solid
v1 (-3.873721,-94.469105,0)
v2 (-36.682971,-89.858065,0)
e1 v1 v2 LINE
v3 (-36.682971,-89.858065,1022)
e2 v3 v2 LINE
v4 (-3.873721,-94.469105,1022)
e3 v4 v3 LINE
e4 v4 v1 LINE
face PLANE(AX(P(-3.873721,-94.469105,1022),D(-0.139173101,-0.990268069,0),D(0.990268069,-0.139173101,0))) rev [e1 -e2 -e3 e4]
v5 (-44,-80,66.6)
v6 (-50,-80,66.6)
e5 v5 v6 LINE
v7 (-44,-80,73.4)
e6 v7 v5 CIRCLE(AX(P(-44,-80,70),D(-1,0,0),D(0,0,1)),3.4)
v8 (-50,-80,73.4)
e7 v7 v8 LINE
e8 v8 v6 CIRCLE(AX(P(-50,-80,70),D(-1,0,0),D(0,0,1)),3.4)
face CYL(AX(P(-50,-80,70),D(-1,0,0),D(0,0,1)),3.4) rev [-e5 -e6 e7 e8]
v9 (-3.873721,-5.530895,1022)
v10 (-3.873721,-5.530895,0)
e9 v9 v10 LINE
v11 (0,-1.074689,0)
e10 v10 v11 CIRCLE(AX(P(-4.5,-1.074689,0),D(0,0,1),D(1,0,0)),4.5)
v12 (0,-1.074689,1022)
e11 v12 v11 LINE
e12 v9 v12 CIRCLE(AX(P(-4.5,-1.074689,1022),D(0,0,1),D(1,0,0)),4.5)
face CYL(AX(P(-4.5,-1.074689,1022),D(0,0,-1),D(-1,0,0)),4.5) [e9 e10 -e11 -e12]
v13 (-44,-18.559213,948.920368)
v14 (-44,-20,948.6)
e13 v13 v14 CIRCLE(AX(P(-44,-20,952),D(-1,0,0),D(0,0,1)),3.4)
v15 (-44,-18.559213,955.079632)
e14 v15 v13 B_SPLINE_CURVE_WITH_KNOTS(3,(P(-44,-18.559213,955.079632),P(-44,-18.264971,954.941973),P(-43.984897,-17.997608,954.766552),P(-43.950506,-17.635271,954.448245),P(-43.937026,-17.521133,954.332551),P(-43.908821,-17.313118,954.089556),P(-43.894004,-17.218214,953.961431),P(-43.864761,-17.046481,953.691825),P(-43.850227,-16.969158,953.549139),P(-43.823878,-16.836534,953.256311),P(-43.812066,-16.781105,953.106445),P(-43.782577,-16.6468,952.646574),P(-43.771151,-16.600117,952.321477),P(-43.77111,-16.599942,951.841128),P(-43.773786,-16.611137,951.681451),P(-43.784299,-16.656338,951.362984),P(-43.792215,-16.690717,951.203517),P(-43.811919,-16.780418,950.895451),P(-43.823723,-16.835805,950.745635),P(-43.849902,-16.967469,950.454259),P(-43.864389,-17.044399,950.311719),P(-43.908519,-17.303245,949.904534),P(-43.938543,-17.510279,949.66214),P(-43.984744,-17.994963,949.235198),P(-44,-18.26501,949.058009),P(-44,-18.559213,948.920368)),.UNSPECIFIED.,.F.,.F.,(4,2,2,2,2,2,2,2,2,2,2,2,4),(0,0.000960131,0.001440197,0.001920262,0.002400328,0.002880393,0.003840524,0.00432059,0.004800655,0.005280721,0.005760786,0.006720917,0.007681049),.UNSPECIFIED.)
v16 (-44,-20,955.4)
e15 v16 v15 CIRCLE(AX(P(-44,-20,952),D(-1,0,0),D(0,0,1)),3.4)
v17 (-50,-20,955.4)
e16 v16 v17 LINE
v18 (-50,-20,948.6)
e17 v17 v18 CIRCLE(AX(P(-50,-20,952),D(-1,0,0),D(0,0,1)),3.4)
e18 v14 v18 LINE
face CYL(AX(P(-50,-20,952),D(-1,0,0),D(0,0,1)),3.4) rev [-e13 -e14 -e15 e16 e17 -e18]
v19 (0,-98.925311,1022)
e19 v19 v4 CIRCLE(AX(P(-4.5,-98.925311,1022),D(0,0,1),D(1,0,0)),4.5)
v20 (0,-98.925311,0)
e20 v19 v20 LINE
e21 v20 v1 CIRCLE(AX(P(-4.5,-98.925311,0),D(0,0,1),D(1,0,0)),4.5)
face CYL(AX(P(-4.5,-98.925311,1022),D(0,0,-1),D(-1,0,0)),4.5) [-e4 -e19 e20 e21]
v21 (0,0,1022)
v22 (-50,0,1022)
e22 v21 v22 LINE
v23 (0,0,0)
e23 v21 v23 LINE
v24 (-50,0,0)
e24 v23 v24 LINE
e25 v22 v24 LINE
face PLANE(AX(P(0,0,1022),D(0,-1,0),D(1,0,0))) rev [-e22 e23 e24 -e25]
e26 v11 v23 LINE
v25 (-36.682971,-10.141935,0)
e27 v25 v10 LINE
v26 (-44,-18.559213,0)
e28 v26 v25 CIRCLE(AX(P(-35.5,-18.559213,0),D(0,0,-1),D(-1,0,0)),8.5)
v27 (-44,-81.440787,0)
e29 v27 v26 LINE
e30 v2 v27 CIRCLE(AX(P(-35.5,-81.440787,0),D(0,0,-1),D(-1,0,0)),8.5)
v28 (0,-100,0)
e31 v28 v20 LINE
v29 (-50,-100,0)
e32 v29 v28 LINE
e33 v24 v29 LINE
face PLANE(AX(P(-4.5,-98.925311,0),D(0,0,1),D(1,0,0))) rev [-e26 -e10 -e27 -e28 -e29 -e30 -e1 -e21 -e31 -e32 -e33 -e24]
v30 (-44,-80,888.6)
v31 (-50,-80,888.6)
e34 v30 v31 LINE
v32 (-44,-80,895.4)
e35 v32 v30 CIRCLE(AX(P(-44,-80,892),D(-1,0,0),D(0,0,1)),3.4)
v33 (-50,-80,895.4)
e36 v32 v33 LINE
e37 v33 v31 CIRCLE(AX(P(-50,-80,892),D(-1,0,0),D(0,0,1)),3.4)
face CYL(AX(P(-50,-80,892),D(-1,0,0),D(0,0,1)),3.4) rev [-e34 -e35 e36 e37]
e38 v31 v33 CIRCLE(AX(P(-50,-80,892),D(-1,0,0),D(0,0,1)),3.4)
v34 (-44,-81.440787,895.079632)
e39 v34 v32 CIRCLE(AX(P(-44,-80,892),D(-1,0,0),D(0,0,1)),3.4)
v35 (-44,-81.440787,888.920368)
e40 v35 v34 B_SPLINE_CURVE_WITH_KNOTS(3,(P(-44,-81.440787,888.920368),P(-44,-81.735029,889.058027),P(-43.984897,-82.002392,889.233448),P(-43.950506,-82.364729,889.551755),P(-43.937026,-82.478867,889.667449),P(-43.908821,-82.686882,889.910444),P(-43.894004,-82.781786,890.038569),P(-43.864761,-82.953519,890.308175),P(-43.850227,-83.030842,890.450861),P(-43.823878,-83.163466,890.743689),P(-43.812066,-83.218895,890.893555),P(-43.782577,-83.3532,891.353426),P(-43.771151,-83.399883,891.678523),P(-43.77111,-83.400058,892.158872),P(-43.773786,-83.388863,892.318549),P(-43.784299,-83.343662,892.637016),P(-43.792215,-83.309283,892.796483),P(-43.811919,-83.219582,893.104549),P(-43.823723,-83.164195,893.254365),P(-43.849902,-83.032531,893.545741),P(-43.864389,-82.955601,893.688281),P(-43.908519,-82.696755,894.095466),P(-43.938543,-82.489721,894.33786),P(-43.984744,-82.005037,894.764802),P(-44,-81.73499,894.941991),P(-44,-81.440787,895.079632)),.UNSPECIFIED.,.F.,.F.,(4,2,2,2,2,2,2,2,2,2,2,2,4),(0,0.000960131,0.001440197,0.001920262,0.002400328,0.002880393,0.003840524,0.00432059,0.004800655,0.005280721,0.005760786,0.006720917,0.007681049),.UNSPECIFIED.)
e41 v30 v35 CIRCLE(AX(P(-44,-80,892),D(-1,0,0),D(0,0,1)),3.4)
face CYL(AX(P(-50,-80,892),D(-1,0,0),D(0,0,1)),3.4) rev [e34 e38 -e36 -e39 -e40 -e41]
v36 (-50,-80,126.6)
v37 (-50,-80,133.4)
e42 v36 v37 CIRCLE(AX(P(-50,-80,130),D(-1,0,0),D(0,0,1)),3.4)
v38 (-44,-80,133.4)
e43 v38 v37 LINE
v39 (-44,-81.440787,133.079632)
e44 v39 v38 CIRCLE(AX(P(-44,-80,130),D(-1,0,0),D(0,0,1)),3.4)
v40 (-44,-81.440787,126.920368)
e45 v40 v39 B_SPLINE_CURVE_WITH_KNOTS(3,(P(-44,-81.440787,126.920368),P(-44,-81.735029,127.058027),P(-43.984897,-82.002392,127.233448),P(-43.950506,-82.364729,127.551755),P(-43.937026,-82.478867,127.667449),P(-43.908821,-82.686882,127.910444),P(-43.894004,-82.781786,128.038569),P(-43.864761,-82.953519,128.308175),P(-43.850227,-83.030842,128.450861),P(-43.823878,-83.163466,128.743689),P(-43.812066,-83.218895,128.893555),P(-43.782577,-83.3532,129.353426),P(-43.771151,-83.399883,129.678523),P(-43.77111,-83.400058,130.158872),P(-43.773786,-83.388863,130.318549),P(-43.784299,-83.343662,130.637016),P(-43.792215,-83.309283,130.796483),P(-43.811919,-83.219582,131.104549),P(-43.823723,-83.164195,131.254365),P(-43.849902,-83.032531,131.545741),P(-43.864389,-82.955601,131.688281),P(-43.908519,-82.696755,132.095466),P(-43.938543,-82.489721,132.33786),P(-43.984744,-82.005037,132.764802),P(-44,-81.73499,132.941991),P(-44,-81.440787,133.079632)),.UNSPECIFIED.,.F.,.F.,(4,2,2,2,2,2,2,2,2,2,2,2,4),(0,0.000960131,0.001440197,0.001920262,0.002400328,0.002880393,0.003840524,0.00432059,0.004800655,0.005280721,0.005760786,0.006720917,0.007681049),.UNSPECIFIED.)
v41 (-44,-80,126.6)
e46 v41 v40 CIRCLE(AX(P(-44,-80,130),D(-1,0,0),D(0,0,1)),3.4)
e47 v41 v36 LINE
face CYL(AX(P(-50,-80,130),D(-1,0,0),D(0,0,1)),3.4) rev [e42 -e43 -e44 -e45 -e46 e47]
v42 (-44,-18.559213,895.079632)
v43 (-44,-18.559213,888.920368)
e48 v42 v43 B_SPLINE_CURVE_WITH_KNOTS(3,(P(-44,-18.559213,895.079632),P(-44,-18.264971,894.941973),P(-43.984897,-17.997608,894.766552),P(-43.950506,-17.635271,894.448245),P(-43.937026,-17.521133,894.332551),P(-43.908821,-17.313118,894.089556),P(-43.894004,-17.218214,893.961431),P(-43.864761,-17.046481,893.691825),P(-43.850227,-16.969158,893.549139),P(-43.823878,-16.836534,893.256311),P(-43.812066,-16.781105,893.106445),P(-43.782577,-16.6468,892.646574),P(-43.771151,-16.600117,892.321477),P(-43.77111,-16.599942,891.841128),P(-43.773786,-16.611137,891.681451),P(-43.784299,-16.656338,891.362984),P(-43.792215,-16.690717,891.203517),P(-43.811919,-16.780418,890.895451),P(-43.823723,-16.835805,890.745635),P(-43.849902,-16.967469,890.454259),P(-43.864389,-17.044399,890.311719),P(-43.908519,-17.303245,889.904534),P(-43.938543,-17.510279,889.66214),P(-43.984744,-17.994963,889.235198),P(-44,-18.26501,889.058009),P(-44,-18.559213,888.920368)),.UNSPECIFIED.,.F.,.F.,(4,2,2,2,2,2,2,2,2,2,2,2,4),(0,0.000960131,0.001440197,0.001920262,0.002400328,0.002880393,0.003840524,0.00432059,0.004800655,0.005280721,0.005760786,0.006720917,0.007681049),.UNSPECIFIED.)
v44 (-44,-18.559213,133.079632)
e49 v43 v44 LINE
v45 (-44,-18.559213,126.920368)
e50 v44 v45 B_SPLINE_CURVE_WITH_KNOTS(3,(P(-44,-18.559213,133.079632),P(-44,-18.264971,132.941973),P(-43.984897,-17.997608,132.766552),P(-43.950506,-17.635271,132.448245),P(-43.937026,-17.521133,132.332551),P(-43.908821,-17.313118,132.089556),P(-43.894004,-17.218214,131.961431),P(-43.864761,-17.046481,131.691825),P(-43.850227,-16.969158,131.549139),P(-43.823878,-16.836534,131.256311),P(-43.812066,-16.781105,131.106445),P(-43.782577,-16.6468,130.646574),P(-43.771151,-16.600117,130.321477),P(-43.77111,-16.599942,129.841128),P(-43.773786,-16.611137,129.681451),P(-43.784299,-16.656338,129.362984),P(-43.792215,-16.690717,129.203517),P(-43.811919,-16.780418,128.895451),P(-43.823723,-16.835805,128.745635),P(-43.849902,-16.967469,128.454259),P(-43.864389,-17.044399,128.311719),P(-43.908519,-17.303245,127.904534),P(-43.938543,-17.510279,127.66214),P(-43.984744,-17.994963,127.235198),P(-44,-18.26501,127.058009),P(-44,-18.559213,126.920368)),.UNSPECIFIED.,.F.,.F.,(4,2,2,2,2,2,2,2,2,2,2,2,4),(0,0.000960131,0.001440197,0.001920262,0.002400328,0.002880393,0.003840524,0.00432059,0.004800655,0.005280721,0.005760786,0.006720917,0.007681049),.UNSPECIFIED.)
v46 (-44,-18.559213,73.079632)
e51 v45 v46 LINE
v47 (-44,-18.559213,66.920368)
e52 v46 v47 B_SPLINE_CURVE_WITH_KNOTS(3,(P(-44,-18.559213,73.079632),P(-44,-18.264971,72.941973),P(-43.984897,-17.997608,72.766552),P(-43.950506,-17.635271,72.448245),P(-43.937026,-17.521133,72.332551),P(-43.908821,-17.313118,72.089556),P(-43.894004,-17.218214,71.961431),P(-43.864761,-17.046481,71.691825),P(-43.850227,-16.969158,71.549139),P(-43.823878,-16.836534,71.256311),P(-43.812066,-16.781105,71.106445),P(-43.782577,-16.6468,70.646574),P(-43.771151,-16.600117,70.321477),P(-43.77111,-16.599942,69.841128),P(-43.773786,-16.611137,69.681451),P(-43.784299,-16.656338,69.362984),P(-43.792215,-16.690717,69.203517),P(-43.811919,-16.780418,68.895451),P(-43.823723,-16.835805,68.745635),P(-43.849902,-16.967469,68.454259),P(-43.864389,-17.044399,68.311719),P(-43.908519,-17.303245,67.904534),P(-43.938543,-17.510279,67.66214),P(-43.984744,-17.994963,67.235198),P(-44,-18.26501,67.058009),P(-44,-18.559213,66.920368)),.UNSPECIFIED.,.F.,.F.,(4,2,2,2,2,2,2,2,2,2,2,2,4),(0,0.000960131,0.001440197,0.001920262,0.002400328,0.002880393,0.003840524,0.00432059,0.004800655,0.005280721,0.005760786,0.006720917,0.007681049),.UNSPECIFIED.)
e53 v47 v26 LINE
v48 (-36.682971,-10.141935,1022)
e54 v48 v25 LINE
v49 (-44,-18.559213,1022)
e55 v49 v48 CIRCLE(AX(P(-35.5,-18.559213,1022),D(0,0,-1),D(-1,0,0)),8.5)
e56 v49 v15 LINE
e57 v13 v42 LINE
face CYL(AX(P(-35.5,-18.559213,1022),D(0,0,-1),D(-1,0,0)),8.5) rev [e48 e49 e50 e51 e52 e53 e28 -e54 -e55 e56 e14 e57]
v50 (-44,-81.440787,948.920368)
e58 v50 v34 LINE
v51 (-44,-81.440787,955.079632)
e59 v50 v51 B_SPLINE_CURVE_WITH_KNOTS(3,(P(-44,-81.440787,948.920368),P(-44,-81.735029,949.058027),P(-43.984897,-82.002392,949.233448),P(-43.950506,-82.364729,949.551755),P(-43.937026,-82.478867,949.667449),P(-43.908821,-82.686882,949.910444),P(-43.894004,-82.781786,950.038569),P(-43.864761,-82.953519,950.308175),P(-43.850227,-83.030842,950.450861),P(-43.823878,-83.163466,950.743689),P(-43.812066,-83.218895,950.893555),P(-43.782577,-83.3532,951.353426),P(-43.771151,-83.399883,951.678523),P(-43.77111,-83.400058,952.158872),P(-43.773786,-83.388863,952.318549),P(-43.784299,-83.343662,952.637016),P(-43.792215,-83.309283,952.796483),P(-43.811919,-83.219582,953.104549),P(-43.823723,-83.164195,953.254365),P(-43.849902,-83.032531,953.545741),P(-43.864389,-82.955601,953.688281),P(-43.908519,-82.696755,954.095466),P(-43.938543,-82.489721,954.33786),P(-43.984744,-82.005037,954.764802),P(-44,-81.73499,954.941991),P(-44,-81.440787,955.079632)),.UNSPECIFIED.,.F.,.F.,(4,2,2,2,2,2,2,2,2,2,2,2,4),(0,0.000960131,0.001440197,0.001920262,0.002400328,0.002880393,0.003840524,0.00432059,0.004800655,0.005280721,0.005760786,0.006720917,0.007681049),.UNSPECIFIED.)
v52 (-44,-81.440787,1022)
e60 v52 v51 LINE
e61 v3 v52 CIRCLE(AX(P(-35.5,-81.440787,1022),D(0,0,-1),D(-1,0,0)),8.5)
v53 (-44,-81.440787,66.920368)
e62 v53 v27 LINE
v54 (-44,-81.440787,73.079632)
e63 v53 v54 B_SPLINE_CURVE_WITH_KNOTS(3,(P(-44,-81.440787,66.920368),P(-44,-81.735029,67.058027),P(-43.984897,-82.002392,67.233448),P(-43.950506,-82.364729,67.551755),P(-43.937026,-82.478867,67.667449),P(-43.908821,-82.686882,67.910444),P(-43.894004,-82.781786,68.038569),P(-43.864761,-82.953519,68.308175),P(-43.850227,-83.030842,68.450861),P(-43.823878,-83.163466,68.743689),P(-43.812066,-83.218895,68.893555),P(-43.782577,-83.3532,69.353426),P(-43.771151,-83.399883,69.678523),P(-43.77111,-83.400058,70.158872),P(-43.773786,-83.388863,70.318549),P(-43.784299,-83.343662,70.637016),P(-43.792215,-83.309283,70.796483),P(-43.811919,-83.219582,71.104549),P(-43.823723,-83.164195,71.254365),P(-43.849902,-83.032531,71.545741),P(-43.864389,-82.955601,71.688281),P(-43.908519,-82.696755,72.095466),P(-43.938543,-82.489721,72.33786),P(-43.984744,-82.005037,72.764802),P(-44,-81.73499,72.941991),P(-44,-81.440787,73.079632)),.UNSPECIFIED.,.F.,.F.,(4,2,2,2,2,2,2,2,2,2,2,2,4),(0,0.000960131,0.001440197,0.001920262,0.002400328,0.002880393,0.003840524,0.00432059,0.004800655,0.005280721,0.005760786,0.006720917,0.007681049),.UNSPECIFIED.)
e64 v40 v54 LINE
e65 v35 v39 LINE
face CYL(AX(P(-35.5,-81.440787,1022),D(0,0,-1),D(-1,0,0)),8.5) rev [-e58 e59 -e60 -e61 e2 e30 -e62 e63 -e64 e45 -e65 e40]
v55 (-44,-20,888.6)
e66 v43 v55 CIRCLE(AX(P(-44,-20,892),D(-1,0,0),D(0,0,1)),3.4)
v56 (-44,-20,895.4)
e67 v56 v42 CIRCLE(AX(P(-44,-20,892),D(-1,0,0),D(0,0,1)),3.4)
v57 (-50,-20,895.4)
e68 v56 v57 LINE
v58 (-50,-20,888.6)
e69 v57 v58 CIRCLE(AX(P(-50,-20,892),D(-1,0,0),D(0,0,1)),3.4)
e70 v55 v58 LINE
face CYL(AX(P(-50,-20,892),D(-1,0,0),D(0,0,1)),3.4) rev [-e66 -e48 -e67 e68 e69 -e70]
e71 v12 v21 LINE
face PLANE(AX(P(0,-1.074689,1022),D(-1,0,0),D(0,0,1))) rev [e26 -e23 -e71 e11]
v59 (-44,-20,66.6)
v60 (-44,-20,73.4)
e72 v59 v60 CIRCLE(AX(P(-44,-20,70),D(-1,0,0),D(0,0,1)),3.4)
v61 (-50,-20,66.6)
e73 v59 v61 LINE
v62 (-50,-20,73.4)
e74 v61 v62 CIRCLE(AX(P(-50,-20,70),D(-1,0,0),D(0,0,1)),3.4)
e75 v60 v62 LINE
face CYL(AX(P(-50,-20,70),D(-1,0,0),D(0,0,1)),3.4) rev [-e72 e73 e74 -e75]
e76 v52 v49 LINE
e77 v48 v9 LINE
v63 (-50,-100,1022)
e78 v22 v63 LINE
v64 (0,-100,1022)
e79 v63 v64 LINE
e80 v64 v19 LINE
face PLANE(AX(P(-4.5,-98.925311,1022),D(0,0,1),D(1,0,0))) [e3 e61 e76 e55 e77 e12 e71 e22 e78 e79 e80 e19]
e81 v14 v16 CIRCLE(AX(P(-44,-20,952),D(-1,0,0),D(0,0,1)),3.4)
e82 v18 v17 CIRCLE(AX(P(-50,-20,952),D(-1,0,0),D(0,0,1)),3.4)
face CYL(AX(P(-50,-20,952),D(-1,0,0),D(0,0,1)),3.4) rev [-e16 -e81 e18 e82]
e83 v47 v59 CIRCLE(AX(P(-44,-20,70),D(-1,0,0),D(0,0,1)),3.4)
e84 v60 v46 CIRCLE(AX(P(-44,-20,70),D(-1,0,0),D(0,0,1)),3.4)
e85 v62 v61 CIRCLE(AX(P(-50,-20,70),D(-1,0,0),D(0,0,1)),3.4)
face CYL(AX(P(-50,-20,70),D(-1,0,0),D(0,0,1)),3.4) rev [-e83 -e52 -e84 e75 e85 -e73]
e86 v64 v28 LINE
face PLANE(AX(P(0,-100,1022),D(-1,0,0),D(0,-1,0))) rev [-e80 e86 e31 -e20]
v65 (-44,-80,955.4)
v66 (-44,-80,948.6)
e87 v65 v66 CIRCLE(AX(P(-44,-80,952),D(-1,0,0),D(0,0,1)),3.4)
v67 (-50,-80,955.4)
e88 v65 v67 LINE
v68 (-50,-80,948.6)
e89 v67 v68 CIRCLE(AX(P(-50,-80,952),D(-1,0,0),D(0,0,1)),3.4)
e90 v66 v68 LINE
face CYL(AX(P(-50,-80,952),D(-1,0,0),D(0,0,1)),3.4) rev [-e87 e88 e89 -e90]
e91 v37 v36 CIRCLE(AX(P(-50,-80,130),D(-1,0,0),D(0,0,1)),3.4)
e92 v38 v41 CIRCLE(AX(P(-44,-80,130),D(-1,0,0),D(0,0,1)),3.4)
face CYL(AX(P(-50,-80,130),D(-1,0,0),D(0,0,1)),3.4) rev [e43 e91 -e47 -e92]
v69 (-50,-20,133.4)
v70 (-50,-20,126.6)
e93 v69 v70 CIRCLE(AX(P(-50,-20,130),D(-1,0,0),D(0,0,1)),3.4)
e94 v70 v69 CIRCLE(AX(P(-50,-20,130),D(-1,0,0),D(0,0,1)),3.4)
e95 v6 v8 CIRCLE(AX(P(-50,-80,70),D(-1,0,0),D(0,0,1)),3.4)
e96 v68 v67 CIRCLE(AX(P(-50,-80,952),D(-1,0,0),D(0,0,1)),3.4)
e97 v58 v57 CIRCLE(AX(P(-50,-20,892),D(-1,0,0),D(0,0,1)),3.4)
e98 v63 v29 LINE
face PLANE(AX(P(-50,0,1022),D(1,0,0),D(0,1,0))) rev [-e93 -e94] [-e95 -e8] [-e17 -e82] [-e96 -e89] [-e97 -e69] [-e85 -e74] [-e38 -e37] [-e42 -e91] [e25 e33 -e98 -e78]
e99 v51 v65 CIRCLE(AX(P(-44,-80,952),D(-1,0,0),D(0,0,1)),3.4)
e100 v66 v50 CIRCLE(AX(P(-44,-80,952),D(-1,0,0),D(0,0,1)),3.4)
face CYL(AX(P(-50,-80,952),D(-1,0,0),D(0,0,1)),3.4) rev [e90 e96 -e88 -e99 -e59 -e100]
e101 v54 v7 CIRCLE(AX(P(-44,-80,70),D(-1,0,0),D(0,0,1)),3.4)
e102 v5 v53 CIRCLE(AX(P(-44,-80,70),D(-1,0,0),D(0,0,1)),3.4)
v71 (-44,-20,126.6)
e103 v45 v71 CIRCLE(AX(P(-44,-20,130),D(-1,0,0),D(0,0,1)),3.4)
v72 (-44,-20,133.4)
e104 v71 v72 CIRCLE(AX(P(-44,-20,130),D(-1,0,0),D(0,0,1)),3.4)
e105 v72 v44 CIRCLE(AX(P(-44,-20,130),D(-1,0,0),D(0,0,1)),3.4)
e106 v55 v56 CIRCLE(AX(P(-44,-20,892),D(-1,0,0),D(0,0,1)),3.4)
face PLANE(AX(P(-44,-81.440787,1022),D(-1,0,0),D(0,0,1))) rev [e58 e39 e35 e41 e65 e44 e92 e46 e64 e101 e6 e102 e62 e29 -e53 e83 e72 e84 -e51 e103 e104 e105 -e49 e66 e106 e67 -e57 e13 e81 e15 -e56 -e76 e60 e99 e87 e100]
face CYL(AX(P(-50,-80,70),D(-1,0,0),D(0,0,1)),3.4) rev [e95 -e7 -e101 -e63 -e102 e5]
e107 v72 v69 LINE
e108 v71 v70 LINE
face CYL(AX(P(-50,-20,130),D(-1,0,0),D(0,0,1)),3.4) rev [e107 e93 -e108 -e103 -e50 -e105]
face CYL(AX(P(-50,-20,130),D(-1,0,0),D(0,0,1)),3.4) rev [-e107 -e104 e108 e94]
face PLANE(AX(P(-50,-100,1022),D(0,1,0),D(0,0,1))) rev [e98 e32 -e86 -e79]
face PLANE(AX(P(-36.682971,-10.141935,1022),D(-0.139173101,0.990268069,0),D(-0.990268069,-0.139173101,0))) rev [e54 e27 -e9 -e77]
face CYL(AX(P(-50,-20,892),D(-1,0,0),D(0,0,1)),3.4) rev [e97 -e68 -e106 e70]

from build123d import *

# Parameters (mm, degrees)
BOSS_EXTRUDE1_DEPTH   = 1022
M8_TAPPED_HOLE1_D     = 6.8
M8_TAPPED_HOLE1_DEPTH = 19.75
M8_TAPPED_HOLE1_TIP   = 2.042926105


with BuildPart() as part:
    # Sketch1 → Boss-Extrude1 (new body)
    with BuildSketch(Plane.XY):
        with BuildLine():
            Line((0, 0), (-50, 0))
            Line((-50, 0), (-50, -100))
            Line((-50, -100), (0, -100))
            Line((0, -100), (0, -98.925311188))
            ThreePointArc((0, -98.925311188), (-1.103806889, -95.973045557), (-3.873721046, -94.469104878))
            Line((-3.873721046, -94.469104878), (-36.682971358, -89.858065454))
            ThreePointArc((-36.682971358, -89.858065454), (-41.915031432, -87.017288616), (-44, -81.440786869))
            Line((-44, -81.440786869), (-44, -18.559213131))
            ThreePointArc((-44, -18.559213131), (-41.915031432, -12.982711384), (-36.682971358, -10.141934546))
            Line((-36.682971358, -10.141934546), (-3.873721046, -5.530895122))
            ThreePointArc((-3.873721046, -5.530895122), (-1.103806889, -4.026954443), (0, -1.074688812))
            Line((0, -1.074688812), (0, 0))
        make_face()
    extrude(amount=BOSS_EXTRUDE1_DEPTH)

    # M8 Tapped Hole1
    with Locations(Plane.ZY.offset(50)):
        with Locations((70, -20), (130, -20), (130, -80), (70, -80), (892, -20), (952, -20), (952, -80), (892, -80)):
            Hole(M8_TAPPED_HOLE1_D / 2, depth=M8_TAPPED_HOLE1_DEPTH)
            with Locations((0, 0, -(M8_TAPPED_HOLE1_DEPTH + M8_TAPPED_HOLE1_TIP / 2))):  # 118° drill point
                Cone(0, M8_TAPPED_HOLE1_D / 2, M8_TAPPED_HOLE1_TIP, mode=Mode.SUBTRACT)


solid = part.part
